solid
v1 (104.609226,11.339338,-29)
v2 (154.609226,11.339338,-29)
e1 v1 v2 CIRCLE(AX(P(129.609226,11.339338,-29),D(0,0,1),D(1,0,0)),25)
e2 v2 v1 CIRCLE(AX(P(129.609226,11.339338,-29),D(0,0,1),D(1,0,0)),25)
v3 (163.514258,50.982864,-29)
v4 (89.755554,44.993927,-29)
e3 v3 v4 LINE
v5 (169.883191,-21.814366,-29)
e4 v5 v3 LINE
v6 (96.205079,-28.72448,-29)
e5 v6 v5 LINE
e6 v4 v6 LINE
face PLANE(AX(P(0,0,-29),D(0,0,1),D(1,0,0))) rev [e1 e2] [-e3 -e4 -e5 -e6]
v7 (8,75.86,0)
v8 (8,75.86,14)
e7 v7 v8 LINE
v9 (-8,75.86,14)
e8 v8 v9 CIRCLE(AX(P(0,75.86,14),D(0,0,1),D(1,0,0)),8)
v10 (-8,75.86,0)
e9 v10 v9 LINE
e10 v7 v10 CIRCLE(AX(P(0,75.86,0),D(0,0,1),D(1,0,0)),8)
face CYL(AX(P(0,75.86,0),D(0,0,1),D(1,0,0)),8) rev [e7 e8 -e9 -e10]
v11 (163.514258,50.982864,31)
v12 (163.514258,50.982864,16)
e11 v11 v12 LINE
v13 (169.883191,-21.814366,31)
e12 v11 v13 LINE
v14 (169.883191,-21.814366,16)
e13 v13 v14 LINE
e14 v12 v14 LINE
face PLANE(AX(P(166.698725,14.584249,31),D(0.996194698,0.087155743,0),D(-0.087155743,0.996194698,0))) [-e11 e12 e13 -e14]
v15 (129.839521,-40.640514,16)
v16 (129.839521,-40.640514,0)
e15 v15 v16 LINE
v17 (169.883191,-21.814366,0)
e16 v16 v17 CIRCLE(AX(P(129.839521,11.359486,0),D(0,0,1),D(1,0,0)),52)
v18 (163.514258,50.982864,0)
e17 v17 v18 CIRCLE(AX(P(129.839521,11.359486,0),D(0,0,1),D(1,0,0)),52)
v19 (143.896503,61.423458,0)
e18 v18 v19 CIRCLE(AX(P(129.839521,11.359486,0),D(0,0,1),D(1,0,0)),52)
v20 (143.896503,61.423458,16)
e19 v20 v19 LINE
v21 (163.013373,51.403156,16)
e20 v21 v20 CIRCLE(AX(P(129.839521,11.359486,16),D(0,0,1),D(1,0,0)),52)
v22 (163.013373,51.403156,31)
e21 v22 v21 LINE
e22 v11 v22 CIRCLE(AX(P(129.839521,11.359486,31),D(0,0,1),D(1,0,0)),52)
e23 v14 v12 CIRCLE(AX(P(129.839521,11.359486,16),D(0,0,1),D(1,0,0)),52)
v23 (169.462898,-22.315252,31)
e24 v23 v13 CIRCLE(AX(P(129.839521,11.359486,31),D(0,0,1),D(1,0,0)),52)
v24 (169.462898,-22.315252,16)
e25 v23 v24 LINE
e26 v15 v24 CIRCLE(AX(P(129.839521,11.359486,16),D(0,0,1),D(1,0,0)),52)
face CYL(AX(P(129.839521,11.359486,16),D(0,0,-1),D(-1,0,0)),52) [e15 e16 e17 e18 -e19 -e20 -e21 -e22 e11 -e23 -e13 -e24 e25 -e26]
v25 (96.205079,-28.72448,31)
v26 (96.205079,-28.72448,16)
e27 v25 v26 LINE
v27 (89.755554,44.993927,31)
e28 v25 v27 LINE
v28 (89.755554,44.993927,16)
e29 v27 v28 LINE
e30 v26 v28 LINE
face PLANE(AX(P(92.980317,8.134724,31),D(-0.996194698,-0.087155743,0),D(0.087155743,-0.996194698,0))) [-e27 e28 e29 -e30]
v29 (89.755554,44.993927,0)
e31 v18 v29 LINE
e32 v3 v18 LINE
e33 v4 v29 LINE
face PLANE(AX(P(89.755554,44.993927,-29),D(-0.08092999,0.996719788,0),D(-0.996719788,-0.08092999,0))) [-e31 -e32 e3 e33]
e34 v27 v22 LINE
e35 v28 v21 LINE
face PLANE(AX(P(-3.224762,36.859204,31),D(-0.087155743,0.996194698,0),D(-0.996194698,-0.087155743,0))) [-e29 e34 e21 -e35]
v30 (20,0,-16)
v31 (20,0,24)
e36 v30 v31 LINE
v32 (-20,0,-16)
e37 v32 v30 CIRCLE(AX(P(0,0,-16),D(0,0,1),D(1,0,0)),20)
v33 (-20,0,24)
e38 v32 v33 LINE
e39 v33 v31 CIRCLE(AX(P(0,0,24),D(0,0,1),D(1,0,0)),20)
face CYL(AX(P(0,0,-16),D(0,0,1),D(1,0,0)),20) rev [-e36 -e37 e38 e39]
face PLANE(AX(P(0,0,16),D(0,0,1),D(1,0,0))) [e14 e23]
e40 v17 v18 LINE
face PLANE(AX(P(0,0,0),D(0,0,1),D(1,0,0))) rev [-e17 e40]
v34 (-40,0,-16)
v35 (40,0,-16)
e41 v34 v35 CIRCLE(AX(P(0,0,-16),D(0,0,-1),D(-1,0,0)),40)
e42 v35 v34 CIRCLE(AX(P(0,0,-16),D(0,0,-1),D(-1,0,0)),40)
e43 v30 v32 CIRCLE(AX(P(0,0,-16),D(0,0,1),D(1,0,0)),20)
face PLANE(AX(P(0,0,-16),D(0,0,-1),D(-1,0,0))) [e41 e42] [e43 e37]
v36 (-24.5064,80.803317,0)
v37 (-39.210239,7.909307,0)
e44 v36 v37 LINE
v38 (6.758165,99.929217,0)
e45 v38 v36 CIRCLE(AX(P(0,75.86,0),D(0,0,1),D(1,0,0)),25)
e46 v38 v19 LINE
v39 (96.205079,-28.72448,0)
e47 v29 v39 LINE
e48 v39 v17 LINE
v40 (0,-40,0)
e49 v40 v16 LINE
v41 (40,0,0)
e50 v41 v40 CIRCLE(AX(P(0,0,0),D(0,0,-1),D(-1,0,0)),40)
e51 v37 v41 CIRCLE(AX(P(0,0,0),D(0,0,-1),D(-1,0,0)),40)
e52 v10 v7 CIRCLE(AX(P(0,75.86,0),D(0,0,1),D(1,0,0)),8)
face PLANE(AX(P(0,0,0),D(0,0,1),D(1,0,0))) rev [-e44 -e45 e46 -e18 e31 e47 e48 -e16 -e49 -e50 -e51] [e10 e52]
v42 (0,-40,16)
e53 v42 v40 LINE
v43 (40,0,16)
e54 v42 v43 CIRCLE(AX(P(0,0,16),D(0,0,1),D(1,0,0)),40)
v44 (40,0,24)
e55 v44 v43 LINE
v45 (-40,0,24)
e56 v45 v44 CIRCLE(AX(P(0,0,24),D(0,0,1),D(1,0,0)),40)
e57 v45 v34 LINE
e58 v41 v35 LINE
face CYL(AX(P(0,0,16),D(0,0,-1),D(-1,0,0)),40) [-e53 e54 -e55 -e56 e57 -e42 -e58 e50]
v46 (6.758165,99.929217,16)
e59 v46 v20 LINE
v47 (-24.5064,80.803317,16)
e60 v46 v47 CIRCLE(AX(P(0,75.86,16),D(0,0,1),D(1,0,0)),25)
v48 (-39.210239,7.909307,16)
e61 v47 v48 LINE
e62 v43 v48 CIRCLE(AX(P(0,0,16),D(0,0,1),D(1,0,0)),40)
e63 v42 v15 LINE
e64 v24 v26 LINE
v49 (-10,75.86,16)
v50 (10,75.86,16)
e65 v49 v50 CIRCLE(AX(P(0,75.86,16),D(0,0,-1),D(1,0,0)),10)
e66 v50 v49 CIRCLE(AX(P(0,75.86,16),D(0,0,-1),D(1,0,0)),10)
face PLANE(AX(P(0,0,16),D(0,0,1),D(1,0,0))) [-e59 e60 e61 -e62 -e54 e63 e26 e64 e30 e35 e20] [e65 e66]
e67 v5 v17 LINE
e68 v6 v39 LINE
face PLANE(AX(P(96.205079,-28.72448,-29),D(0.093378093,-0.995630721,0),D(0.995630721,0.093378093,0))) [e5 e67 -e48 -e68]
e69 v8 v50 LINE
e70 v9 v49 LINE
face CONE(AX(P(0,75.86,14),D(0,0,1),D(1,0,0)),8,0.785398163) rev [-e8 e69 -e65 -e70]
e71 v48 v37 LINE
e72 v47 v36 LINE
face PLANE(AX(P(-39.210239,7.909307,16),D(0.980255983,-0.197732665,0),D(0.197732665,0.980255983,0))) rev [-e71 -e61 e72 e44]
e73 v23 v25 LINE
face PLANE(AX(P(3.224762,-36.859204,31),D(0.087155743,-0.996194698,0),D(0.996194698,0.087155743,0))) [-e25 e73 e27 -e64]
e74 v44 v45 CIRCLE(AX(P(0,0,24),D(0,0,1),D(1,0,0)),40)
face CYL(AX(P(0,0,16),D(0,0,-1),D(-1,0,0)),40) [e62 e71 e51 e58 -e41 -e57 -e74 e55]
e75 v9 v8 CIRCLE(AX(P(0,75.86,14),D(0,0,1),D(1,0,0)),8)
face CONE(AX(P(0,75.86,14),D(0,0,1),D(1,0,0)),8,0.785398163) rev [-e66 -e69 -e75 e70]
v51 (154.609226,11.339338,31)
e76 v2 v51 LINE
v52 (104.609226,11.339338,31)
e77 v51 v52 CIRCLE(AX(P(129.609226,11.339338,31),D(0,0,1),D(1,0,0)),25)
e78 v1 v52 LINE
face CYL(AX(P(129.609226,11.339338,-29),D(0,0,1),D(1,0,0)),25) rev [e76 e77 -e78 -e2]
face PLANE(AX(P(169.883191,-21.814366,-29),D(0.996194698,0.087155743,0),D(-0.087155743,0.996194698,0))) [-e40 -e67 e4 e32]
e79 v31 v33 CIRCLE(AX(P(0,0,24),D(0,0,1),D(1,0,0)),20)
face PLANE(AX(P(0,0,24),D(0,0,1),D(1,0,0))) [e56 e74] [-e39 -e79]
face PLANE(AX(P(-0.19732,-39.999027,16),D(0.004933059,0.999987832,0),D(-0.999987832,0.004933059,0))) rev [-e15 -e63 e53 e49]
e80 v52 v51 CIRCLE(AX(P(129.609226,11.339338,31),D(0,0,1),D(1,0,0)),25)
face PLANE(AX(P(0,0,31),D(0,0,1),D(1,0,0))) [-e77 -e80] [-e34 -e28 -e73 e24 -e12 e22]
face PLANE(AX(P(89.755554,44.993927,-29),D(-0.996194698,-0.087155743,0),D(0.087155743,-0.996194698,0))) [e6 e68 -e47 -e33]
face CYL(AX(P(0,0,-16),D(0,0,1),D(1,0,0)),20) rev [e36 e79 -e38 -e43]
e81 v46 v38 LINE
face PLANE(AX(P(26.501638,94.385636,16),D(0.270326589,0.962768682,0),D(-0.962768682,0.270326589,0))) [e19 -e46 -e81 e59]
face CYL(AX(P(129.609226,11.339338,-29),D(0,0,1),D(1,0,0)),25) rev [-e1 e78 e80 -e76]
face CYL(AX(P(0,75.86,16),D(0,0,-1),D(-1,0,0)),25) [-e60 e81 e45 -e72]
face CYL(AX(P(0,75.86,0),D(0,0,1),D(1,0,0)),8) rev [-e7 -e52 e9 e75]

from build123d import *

# Parameters (mm, degrees)
LEVER_PLATE_DEPTH           = 16
FRONT_HUB_SKETCH_40_R       = 40
FRONT_PIVOT_HUB_40_DEPTH    = 8
REAR_START                  = 16
REAR_HUB_SKETCH_40_R        = 40
REAR_PIVOT_HUB_40_DEPTH     = 16
SMALL_HOLE_SKETCH_8_R       = 8
SMALL_HOLE_8_DEPTH          = 16
SMALL_HOLE_CHAMFER_2MM_SIZE = 2
EYE_PAD_74X74_DEPTH         = 15
EYE_BLOCK_DEPTH             = 60
EYE_BORE_SKETCH_25_R        = 25
EYE_BORE_25_DEPTH           = 60
PIVOT_BORE_SKETCH_20_R      = 20
PIVOT_BORE_20_DEPTH         = 40


with BuildPart() as part:
    # Lever Plate Profile → Lever Plate (new body)
    with BuildSketch(Plane.XY):
        with BuildLine():
            Line((143.896503384, 61.42345762), (6.758164717, 99.929217055))
            ThreePointArc((6.758164717, 99.929217055), (-13.046071322, 97.186040961), (-24.506399585, 80.803316636))
            Line((-24.506399585, 80.803316636), (-39.210239337, 7.909306617))
            ThreePointArc((-39.210239337, 7.909306617), (-30.954581767, -25.334045623), (0, -40))
            Line((0, -40), (129.839520773, -40.640513855))
            ThreePointArc((129.839520773, -40.640513855), (181.3532399, 4.26464706), (143.896503384, 61.42345762))
        make_face()
    extrude(amount=LEVER_PLATE_DEPTH)

    # Front Hub Sketch Ø40 → Front Pivot Hub Ø40 (add)
    with BuildSketch(Plane.XY.offset(16)):
        with Locations(Location((0, 0, 0), (0, 0, 168.595597299))):
            Circle(FRONT_HUB_SKETCH_40_R)
    extrude(amount=FRONT_PIVOT_HUB_40_DEPTH)

    # Rear Hub Sketch Ø40 → Rear Pivot Hub Ø40 (add)
    with BuildSketch(Plane(origin=(0, 0, 0), x_dir=(-1, 0, 0), z_dir=(0, 0, -1)).offset(REAR_START)):
        Circle(REAR_HUB_SKETCH_40_R)
    extrude(amount=-REAR_PIVOT_HUB_40_DEPTH)

    # Small Hole Sketch Ø8 → Small Hole Ø8 (cut)
    with BuildSketch(Plane.XY.offset(16)):
        with Locations((0, 75.86)):
            Circle(SMALL_HOLE_SKETCH_8_R)
    extrude(amount=-SMALL_HOLE_8_DEPTH, mode=Mode.SUBTRACT)

    # Small Hole Chamfer 2mm
    small_hole_chamfer_2mm_edges = [part.edges().sort_by_distance(p)[0] for p in [
        (-8, 75.86, 16),
    ]]
    chamfer(small_hole_chamfer_2mm_edges, length=SMALL_HOLE_CHAMFER_2MM_SIZE)

    # Eye Pad Sketch 74x74 → Eye Pad 74x74 (add)
    with BuildSketch(Plane.XY.offset(16)):
        Polygon((92.980316943, 8.134723664), (129.839520773, 11.359486145), (126.614758291, 48.218689975), (89.755554462, 44.993927493), align=None)
        Polygon((126.614758291, 48.218689975), (129.839520773, 11.359486145), (129.839520773, 48.500820134), align=None)
        with BuildLine():
            Line((129.839520773, 48.500820134), (129.839520773, 11.359486145))
            Line((129.839520773, 11.359486145), (92.980316943, 8.134723664))
            Line((92.980316943, 8.134723664), (96.205079425, -28.724480166))
            Line((96.205079425, -28.724480166), (169.462898271, -22.315251502))
            ThreePointArc((169.462898271, -22.315251502), (169.673831815, -22.065469558), (169.883190784, -21.81436639))
            Line((169.883190784, -21.81436639), (163.51425842, 50.982863644))
            ThreePointArc((163.51425842, 50.982863644), (163.264476476, 51.193797187), (163.013373308, 51.403156157))
            Line((163.013373308, 51.403156157), (129.839520773, 48.500820134))
        make_face()
    extrude(amount=EYE_PAD_74X74_DEPTH)

    # Eye Block Sketch → Eye Block (add)
    with BuildSketch(Plane.XY.offset(31)):
        Polygon((89.755554462, 44.993927493), (163.51425842, 50.982863644), (169.883190784, -21.81436639), (96.205079425, -28.724480166), align=None)
    extrude(amount=-EYE_BLOCK_DEPTH)

    # Eye Bore Sketch Ø25 → Eye Bore Ø25 (cut)
    with BuildSketch(Plane.XY.offset(31)):
        with Locations((129.609226366, 11.339337995)):
            Circle(EYE_BORE_SKETCH_25_R)
    extrude(amount=-EYE_BORE_25_DEPTH, mode=Mode.SUBTRACT)

    # Pivot Bore Sketch Ø20 → Pivot Bore Ø20 (cut)
    with BuildSketch(Plane.XY.offset(24)):
        Circle(PIVOT_BORE_SKETCH_20_R)
    extrude(amount=-PIVOT_BORE_20_DEPTH, mode=Mode.SUBTRACT)


solid = part.part
